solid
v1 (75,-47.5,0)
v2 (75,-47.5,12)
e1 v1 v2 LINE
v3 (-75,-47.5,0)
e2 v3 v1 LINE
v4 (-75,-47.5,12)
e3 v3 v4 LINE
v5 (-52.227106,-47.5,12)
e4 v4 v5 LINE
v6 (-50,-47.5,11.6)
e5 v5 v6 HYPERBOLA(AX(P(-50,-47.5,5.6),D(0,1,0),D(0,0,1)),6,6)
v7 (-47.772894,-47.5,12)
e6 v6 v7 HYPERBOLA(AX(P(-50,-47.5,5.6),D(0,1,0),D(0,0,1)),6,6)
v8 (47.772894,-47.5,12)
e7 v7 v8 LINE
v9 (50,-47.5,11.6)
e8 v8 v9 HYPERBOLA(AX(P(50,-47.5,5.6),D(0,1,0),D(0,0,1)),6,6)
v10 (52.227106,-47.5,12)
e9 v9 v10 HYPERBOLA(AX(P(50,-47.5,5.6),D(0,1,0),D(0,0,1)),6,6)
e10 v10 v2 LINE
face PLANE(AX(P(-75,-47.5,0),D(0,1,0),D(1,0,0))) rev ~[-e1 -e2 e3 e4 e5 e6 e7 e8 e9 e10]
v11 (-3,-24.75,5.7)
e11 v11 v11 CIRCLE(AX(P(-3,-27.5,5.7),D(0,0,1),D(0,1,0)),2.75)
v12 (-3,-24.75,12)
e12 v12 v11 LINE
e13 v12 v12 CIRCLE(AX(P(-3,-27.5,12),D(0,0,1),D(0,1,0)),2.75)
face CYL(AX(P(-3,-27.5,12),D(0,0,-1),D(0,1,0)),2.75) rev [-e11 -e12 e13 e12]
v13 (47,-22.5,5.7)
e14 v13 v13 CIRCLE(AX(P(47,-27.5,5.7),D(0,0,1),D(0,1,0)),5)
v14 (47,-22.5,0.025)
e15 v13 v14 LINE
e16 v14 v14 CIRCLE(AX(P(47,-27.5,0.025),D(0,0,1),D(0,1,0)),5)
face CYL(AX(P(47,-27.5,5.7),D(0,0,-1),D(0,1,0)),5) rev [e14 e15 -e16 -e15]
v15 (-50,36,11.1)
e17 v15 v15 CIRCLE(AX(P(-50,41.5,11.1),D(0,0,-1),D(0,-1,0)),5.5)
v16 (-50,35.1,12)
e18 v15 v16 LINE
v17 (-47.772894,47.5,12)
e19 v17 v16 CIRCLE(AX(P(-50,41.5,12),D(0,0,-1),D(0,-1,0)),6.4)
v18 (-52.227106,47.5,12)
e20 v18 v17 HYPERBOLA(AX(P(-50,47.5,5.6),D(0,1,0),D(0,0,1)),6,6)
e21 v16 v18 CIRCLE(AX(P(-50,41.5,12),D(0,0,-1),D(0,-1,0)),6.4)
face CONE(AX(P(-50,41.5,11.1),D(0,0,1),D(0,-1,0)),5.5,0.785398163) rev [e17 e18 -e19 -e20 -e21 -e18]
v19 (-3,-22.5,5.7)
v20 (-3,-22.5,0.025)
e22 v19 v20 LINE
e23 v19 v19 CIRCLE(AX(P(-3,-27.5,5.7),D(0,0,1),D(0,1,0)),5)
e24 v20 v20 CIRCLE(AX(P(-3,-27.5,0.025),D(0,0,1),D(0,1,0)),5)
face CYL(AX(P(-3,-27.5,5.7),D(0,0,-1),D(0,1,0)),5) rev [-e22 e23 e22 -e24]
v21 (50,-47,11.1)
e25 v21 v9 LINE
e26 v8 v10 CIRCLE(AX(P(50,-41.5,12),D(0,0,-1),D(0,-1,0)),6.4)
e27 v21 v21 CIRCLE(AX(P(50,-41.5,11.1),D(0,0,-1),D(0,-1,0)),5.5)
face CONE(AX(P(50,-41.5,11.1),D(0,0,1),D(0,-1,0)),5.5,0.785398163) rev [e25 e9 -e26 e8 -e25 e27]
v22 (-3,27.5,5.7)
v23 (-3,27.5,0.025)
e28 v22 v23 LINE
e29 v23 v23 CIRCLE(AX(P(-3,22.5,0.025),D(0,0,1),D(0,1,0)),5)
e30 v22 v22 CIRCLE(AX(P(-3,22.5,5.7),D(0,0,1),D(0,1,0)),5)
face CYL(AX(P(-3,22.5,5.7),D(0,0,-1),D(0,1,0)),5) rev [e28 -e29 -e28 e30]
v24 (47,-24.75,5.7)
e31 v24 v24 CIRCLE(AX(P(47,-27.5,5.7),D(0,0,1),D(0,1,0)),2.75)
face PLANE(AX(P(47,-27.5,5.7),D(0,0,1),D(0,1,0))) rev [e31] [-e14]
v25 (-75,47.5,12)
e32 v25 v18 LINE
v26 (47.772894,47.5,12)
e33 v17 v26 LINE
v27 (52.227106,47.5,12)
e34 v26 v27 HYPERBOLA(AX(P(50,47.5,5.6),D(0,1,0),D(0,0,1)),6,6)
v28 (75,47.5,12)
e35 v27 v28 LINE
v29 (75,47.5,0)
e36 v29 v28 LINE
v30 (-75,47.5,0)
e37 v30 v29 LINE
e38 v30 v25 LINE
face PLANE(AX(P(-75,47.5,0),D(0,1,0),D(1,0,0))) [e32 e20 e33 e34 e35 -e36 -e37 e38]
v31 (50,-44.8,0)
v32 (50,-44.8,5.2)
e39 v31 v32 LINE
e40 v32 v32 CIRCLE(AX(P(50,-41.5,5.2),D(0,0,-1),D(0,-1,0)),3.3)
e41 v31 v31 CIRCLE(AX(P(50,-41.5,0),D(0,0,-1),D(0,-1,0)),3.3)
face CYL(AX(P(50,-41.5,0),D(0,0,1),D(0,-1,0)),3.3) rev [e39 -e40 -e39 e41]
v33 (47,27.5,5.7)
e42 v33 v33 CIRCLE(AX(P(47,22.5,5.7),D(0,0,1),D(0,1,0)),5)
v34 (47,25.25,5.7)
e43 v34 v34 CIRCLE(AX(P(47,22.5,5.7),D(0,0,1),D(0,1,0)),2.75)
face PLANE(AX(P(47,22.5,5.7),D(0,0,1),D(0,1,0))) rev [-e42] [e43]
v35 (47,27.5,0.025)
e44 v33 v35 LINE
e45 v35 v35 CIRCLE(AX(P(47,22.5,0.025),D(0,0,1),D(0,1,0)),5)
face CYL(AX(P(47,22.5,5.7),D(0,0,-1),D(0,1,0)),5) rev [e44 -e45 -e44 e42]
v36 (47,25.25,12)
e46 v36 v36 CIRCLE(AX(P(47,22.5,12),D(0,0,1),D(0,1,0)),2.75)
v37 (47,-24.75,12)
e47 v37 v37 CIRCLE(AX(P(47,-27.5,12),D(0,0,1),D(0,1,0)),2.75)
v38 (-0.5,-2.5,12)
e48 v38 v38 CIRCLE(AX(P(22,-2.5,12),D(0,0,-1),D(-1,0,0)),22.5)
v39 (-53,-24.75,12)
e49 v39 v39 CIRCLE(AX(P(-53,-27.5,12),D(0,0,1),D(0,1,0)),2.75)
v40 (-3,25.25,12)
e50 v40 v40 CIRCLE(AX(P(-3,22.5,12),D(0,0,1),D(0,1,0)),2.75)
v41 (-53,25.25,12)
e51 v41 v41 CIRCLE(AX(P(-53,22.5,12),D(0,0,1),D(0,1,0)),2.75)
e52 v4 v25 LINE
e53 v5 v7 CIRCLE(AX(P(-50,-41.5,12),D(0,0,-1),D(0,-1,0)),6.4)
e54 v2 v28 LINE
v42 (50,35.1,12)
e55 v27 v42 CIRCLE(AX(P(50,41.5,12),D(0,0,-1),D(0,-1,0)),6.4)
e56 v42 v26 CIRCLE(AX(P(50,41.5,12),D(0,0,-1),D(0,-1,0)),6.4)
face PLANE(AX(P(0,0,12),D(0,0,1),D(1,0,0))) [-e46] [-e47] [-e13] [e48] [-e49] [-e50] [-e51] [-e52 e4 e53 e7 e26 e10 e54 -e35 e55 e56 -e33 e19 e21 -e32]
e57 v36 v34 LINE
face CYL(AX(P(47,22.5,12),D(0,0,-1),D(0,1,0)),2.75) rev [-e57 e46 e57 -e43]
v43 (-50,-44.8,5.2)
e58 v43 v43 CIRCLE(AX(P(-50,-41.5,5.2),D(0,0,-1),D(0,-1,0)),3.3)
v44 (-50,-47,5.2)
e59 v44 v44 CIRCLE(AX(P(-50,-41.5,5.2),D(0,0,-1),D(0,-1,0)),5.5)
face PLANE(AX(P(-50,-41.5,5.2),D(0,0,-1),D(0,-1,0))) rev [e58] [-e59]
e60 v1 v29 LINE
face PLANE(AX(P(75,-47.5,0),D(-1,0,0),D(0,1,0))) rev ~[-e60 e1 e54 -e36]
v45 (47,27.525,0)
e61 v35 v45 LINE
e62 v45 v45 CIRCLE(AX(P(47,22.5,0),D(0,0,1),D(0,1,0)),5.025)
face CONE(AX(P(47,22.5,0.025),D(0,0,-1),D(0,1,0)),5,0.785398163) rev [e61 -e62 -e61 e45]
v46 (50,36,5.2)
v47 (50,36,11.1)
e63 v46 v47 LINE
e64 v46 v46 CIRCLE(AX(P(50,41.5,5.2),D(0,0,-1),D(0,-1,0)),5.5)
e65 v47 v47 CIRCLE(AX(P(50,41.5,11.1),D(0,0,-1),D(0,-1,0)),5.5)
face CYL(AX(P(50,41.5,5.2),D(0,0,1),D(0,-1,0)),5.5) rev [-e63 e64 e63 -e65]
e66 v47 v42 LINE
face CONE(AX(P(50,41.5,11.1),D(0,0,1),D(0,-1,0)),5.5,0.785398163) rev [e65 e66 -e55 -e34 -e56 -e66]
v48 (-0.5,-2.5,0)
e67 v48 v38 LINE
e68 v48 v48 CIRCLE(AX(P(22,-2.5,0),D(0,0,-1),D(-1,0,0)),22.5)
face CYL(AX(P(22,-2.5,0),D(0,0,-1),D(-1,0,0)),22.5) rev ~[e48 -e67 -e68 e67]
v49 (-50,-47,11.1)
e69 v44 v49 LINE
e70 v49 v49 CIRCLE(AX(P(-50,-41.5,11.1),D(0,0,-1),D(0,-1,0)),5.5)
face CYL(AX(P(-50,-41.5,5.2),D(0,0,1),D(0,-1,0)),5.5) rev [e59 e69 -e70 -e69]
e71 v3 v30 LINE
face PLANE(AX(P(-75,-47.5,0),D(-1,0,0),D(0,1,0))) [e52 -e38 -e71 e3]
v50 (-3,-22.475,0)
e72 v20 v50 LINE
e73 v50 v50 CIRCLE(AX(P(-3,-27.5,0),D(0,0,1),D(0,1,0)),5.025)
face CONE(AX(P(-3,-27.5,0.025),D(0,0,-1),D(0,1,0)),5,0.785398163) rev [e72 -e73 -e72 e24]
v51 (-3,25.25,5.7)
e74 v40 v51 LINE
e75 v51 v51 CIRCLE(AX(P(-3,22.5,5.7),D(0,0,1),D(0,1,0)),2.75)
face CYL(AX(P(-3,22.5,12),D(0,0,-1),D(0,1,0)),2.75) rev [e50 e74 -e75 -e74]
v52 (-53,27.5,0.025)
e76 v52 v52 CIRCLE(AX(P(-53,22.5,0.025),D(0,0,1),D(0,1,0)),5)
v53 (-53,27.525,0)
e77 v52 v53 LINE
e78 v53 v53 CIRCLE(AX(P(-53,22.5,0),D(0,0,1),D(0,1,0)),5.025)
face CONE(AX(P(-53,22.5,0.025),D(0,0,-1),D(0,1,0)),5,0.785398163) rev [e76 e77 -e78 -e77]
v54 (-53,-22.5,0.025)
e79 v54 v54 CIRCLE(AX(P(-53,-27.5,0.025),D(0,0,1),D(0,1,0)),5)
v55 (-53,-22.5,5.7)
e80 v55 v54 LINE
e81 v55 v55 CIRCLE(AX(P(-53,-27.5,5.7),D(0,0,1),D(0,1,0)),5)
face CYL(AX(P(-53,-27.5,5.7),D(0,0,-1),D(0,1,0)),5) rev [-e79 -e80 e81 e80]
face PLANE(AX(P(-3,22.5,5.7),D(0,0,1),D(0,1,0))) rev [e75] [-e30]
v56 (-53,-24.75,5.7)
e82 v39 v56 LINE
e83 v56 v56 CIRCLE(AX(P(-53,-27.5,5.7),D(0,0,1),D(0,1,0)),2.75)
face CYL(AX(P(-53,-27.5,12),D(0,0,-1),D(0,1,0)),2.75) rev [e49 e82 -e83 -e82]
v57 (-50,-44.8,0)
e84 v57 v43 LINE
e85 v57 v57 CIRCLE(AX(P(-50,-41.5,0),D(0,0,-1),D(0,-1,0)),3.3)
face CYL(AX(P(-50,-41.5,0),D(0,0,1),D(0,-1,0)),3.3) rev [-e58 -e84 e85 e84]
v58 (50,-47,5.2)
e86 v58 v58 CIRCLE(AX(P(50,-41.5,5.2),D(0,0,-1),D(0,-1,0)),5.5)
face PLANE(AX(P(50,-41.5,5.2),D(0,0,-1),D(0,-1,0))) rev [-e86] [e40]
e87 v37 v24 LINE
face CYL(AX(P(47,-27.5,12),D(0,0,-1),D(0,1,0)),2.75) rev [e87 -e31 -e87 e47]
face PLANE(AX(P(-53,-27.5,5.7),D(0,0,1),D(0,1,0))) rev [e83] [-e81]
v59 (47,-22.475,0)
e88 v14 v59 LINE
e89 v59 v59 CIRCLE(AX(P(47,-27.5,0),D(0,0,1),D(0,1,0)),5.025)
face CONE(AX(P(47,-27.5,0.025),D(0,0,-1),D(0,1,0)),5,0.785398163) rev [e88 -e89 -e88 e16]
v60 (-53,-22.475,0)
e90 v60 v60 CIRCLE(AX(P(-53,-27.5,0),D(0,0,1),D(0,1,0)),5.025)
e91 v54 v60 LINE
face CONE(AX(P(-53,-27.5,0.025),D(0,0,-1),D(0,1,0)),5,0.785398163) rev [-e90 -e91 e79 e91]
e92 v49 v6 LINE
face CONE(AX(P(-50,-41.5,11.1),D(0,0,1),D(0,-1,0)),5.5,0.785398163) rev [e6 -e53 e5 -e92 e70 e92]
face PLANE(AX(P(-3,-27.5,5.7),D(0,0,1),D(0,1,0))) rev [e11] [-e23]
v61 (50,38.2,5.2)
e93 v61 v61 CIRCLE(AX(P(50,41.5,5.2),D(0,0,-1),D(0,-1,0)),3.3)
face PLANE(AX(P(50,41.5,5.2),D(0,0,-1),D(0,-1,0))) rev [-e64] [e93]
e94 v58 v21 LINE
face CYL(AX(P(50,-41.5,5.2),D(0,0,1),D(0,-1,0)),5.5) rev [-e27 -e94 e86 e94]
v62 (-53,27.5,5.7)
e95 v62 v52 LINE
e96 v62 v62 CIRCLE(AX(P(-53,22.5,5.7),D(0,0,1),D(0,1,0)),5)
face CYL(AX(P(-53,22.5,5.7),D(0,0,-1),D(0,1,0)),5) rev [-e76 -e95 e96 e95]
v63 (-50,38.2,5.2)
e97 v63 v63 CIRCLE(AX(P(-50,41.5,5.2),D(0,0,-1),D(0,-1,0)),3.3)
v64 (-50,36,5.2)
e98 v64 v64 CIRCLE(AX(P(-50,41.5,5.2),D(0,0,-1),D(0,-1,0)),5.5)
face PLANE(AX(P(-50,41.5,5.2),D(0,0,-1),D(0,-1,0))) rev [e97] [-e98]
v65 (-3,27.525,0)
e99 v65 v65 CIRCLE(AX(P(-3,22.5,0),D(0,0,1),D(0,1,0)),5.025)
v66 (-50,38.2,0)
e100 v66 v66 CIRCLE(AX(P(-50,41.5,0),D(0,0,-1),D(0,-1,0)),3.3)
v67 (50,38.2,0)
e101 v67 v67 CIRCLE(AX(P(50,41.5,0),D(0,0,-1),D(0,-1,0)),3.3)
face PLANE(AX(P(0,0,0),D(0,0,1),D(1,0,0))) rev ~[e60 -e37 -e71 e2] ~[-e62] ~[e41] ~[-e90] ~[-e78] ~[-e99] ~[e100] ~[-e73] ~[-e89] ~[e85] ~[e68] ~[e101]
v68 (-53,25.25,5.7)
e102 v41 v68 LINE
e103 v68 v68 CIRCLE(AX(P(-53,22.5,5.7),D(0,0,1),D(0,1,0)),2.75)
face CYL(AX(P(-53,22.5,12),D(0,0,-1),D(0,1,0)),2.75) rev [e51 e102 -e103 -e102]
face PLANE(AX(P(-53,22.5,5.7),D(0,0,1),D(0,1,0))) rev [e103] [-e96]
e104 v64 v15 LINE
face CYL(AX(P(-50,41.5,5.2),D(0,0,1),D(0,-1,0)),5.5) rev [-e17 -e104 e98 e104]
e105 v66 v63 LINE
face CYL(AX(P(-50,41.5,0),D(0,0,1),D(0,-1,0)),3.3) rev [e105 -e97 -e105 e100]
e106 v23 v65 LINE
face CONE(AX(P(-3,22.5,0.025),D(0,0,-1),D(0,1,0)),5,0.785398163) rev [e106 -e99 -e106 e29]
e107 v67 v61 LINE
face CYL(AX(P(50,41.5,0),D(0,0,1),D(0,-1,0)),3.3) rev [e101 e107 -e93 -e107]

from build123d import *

# Parameters (mm, degrees)
SKETCH_1_W               = 150
SKETCH_1_H               = 95
EXTRUDE_1_DEPTH          = 12
HOLE_WIZARD_1_AT_2_COUNT = 2
HOLE_WIZARD_1_AT_2_PITCH = 100
HOLE_WIZARD_1_AT_3_COUNT = 2
HOLE_WIZARD_1_AT_3_PITCH = 83
HOLE_WIZARD_1_AT_4_COUNT = 2
HOLE_WIZARD_1_AT_4_PITCH = 129.957685421
HOLE_WIZARD_2_AT_2_COUNT = 2
HOLE_WIZARD_2_AT_2_PITCH = 50
HOLE_WIZARD_2_AT_3_COUNT = 2
HOLE_WIZARD_2_AT_3_PITCH = 100
HOLE_WIZARD_2_AT_4_COUNT = 2
HOLE_WIZARD_2_AT_4_PITCH = 111.803398875
HOLE_WIZARD_2_AT_5_COUNT = 2
HOLE_WIZARD_2_AT_5_PITCH = 70.710678119
HOLE_WIZARD_2_AT_6_COUNT = 2
HOLE_WIZARD_2_AT_6_PITCH = 50
SKETCH_9_R               = 22.5
CUT_EXTRUDE_1_DEPTH      = 90.583759689


with BuildPart() as part:
    # 草图1 → 凸台-拉伸1 (new body)
    with BuildSketch(Plane.XY):
        Rectangle(SKETCH_1_W, SKETCH_1_H)
    extrude(amount=EXTRUDE_1_DEPTH)

    # 草图6 → 打孔尺寸(%根据)内六角圆柱头螺钉的类型1 (revolve, cut)
    with BuildSketch(Plane(origin=(-50, -41.5, 12), x_dir=(0, -1, 0), z_dir=(1, 0, 0))):
        Polygon((0, 0), (0, 12), (3.3, 12), (3.3, 6.8), (5.5, 6.8), (5.5, 0.9), (6.4, 0), align=None)
    hole_wizard_1 = revolve(axis=Axis((-50, -41.5, 18.35), (0, 0, -1)), mode=Mode.SUBTRACT)

    # 打孔尺寸(%根据)内六角圆柱头螺钉的类型1 at 2: 打孔尺寸(%根据)内六角圆柱头螺钉的类型1 ×2
    with Locations(*[(i * HOLE_WIZARD_1_AT_2_PITCH, 0, 0) for i in range(1, HOLE_WIZARD_1_AT_2_COUNT)]):
        add(hole_wizard_1, mode=Mode.SUBTRACT)

    # 打孔尺寸(%根据)内六角圆柱头螺钉的类型1 at 3: 打孔尺寸(%根据)内六角圆柱头螺钉的类型1 ×2
    with Locations(*[(0, i * HOLE_WIZARD_1_AT_3_PITCH, 0) for i in range(1, HOLE_WIZARD_1_AT_3_COUNT)]):
        add(hole_wizard_1, mode=Mode.SUBTRACT)

    # 打孔尺寸(%根据)内六角圆柱头螺钉的类型1 at 4: 打孔尺寸(%根据)内六角圆柱头螺钉的类型1 ×2
    with Locations(*[Vector(0.7694812328797624, 0.6386694232902033, 0) * (i * HOLE_WIZARD_1_AT_4_PITCH) for i in range(1, HOLE_WIZARD_1_AT_4_COUNT)]):
        add(hole_wizard_1, mode=Mode.SUBTRACT)

    # 草图8 → 打孔尺寸(%根据)内六角圆柱头螺钉的类型2 (revolve, cut)
    with BuildSketch(Plane(origin=(-53, -27.5, 0), x_dir=(0, 1, 0), z_dir=(1, 0, 0))):
        Polygon((0, 0), (0, 12), (2.75, 12), (2.75, 5.7), (5, 5.7), (5, 0.025), (5.025, 0), align=None)
    hole_wizard_2 = revolve(axis=Axis((-53, -27.5, -6.35), (0, 0, 1)), mode=Mode.SUBTRACT)

    # 打孔尺寸(%根据)内六角圆柱头螺钉的类型2 at 2: 打孔尺寸(%根据)内六角圆柱头螺钉的类型2 ×2
    with Locations(*[(i * HOLE_WIZARD_2_AT_2_PITCH, 0, 0) for i in range(1, HOLE_WIZARD_2_AT_2_COUNT)]):
        add(hole_wizard_2, mode=Mode.SUBTRACT)

    # 打孔尺寸(%根据)内六角圆柱头螺钉的类型2 at 3: 打孔尺寸(%根据)内六角圆柱头螺钉的类型2 ×2
    with Locations(*[(i * HOLE_WIZARD_2_AT_3_PITCH, 0, 0) for i in range(1, HOLE_WIZARD_2_AT_3_COUNT)]):
        add(hole_wizard_2, mode=Mode.SUBTRACT)

    # 打孔尺寸(%根据)内六角圆柱头螺钉的类型2 at 4: 打孔尺寸(%根据)内六角圆柱头螺钉的类型2 ×2
    with Locations(*[Vector(0.8944271909999156, 0.4472135954999584, 0) * (i * HOLE_WIZARD_2_AT_4_PITCH) for i in range(1, HOLE_WIZARD_2_AT_4_COUNT)]):
        add(hole_wizard_2, mode=Mode.SUBTRACT)

    # 打孔尺寸(%根据)内六角圆柱头螺钉的类型2 at 5: 打孔尺寸(%根据)内六角圆柱头螺钉的类型2 ×2
    with Locations(*[Vector(0.7071067811865471, 0.7071067811865479, 0) * (i * HOLE_WIZARD_2_AT_5_PITCH) for i in range(1, HOLE_WIZARD_2_AT_5_COUNT)]):
        add(hole_wizard_2, mode=Mode.SUBTRACT)

    # 打孔尺寸(%根据)内六角圆柱头螺钉的类型2 at 6: 打孔尺寸(%根据)内六角圆柱头螺钉的类型2 ×2
    with Locations(*[(0, i * HOLE_WIZARD_2_AT_6_PITCH, 0) for i in range(1, HOLE_WIZARD_2_AT_6_COUNT)]):
        add(hole_wizard_2, mode=Mode.SUBTRACT)

    # 草图9 → 切除-拉伸1 (cut, through all)
    with BuildSketch(Plane(origin=(0, 0, 0), x_dir=(-1, 0, 0), z_dir=(0, 0, -1))):
        with Locations((-22, -2.5)):
            Circle(SKETCH_9_R)
    extrude(amount=-CUT_EXTRUDE_1_DEPTH, mode=Mode.SUBTRACT)


solid = part.part
